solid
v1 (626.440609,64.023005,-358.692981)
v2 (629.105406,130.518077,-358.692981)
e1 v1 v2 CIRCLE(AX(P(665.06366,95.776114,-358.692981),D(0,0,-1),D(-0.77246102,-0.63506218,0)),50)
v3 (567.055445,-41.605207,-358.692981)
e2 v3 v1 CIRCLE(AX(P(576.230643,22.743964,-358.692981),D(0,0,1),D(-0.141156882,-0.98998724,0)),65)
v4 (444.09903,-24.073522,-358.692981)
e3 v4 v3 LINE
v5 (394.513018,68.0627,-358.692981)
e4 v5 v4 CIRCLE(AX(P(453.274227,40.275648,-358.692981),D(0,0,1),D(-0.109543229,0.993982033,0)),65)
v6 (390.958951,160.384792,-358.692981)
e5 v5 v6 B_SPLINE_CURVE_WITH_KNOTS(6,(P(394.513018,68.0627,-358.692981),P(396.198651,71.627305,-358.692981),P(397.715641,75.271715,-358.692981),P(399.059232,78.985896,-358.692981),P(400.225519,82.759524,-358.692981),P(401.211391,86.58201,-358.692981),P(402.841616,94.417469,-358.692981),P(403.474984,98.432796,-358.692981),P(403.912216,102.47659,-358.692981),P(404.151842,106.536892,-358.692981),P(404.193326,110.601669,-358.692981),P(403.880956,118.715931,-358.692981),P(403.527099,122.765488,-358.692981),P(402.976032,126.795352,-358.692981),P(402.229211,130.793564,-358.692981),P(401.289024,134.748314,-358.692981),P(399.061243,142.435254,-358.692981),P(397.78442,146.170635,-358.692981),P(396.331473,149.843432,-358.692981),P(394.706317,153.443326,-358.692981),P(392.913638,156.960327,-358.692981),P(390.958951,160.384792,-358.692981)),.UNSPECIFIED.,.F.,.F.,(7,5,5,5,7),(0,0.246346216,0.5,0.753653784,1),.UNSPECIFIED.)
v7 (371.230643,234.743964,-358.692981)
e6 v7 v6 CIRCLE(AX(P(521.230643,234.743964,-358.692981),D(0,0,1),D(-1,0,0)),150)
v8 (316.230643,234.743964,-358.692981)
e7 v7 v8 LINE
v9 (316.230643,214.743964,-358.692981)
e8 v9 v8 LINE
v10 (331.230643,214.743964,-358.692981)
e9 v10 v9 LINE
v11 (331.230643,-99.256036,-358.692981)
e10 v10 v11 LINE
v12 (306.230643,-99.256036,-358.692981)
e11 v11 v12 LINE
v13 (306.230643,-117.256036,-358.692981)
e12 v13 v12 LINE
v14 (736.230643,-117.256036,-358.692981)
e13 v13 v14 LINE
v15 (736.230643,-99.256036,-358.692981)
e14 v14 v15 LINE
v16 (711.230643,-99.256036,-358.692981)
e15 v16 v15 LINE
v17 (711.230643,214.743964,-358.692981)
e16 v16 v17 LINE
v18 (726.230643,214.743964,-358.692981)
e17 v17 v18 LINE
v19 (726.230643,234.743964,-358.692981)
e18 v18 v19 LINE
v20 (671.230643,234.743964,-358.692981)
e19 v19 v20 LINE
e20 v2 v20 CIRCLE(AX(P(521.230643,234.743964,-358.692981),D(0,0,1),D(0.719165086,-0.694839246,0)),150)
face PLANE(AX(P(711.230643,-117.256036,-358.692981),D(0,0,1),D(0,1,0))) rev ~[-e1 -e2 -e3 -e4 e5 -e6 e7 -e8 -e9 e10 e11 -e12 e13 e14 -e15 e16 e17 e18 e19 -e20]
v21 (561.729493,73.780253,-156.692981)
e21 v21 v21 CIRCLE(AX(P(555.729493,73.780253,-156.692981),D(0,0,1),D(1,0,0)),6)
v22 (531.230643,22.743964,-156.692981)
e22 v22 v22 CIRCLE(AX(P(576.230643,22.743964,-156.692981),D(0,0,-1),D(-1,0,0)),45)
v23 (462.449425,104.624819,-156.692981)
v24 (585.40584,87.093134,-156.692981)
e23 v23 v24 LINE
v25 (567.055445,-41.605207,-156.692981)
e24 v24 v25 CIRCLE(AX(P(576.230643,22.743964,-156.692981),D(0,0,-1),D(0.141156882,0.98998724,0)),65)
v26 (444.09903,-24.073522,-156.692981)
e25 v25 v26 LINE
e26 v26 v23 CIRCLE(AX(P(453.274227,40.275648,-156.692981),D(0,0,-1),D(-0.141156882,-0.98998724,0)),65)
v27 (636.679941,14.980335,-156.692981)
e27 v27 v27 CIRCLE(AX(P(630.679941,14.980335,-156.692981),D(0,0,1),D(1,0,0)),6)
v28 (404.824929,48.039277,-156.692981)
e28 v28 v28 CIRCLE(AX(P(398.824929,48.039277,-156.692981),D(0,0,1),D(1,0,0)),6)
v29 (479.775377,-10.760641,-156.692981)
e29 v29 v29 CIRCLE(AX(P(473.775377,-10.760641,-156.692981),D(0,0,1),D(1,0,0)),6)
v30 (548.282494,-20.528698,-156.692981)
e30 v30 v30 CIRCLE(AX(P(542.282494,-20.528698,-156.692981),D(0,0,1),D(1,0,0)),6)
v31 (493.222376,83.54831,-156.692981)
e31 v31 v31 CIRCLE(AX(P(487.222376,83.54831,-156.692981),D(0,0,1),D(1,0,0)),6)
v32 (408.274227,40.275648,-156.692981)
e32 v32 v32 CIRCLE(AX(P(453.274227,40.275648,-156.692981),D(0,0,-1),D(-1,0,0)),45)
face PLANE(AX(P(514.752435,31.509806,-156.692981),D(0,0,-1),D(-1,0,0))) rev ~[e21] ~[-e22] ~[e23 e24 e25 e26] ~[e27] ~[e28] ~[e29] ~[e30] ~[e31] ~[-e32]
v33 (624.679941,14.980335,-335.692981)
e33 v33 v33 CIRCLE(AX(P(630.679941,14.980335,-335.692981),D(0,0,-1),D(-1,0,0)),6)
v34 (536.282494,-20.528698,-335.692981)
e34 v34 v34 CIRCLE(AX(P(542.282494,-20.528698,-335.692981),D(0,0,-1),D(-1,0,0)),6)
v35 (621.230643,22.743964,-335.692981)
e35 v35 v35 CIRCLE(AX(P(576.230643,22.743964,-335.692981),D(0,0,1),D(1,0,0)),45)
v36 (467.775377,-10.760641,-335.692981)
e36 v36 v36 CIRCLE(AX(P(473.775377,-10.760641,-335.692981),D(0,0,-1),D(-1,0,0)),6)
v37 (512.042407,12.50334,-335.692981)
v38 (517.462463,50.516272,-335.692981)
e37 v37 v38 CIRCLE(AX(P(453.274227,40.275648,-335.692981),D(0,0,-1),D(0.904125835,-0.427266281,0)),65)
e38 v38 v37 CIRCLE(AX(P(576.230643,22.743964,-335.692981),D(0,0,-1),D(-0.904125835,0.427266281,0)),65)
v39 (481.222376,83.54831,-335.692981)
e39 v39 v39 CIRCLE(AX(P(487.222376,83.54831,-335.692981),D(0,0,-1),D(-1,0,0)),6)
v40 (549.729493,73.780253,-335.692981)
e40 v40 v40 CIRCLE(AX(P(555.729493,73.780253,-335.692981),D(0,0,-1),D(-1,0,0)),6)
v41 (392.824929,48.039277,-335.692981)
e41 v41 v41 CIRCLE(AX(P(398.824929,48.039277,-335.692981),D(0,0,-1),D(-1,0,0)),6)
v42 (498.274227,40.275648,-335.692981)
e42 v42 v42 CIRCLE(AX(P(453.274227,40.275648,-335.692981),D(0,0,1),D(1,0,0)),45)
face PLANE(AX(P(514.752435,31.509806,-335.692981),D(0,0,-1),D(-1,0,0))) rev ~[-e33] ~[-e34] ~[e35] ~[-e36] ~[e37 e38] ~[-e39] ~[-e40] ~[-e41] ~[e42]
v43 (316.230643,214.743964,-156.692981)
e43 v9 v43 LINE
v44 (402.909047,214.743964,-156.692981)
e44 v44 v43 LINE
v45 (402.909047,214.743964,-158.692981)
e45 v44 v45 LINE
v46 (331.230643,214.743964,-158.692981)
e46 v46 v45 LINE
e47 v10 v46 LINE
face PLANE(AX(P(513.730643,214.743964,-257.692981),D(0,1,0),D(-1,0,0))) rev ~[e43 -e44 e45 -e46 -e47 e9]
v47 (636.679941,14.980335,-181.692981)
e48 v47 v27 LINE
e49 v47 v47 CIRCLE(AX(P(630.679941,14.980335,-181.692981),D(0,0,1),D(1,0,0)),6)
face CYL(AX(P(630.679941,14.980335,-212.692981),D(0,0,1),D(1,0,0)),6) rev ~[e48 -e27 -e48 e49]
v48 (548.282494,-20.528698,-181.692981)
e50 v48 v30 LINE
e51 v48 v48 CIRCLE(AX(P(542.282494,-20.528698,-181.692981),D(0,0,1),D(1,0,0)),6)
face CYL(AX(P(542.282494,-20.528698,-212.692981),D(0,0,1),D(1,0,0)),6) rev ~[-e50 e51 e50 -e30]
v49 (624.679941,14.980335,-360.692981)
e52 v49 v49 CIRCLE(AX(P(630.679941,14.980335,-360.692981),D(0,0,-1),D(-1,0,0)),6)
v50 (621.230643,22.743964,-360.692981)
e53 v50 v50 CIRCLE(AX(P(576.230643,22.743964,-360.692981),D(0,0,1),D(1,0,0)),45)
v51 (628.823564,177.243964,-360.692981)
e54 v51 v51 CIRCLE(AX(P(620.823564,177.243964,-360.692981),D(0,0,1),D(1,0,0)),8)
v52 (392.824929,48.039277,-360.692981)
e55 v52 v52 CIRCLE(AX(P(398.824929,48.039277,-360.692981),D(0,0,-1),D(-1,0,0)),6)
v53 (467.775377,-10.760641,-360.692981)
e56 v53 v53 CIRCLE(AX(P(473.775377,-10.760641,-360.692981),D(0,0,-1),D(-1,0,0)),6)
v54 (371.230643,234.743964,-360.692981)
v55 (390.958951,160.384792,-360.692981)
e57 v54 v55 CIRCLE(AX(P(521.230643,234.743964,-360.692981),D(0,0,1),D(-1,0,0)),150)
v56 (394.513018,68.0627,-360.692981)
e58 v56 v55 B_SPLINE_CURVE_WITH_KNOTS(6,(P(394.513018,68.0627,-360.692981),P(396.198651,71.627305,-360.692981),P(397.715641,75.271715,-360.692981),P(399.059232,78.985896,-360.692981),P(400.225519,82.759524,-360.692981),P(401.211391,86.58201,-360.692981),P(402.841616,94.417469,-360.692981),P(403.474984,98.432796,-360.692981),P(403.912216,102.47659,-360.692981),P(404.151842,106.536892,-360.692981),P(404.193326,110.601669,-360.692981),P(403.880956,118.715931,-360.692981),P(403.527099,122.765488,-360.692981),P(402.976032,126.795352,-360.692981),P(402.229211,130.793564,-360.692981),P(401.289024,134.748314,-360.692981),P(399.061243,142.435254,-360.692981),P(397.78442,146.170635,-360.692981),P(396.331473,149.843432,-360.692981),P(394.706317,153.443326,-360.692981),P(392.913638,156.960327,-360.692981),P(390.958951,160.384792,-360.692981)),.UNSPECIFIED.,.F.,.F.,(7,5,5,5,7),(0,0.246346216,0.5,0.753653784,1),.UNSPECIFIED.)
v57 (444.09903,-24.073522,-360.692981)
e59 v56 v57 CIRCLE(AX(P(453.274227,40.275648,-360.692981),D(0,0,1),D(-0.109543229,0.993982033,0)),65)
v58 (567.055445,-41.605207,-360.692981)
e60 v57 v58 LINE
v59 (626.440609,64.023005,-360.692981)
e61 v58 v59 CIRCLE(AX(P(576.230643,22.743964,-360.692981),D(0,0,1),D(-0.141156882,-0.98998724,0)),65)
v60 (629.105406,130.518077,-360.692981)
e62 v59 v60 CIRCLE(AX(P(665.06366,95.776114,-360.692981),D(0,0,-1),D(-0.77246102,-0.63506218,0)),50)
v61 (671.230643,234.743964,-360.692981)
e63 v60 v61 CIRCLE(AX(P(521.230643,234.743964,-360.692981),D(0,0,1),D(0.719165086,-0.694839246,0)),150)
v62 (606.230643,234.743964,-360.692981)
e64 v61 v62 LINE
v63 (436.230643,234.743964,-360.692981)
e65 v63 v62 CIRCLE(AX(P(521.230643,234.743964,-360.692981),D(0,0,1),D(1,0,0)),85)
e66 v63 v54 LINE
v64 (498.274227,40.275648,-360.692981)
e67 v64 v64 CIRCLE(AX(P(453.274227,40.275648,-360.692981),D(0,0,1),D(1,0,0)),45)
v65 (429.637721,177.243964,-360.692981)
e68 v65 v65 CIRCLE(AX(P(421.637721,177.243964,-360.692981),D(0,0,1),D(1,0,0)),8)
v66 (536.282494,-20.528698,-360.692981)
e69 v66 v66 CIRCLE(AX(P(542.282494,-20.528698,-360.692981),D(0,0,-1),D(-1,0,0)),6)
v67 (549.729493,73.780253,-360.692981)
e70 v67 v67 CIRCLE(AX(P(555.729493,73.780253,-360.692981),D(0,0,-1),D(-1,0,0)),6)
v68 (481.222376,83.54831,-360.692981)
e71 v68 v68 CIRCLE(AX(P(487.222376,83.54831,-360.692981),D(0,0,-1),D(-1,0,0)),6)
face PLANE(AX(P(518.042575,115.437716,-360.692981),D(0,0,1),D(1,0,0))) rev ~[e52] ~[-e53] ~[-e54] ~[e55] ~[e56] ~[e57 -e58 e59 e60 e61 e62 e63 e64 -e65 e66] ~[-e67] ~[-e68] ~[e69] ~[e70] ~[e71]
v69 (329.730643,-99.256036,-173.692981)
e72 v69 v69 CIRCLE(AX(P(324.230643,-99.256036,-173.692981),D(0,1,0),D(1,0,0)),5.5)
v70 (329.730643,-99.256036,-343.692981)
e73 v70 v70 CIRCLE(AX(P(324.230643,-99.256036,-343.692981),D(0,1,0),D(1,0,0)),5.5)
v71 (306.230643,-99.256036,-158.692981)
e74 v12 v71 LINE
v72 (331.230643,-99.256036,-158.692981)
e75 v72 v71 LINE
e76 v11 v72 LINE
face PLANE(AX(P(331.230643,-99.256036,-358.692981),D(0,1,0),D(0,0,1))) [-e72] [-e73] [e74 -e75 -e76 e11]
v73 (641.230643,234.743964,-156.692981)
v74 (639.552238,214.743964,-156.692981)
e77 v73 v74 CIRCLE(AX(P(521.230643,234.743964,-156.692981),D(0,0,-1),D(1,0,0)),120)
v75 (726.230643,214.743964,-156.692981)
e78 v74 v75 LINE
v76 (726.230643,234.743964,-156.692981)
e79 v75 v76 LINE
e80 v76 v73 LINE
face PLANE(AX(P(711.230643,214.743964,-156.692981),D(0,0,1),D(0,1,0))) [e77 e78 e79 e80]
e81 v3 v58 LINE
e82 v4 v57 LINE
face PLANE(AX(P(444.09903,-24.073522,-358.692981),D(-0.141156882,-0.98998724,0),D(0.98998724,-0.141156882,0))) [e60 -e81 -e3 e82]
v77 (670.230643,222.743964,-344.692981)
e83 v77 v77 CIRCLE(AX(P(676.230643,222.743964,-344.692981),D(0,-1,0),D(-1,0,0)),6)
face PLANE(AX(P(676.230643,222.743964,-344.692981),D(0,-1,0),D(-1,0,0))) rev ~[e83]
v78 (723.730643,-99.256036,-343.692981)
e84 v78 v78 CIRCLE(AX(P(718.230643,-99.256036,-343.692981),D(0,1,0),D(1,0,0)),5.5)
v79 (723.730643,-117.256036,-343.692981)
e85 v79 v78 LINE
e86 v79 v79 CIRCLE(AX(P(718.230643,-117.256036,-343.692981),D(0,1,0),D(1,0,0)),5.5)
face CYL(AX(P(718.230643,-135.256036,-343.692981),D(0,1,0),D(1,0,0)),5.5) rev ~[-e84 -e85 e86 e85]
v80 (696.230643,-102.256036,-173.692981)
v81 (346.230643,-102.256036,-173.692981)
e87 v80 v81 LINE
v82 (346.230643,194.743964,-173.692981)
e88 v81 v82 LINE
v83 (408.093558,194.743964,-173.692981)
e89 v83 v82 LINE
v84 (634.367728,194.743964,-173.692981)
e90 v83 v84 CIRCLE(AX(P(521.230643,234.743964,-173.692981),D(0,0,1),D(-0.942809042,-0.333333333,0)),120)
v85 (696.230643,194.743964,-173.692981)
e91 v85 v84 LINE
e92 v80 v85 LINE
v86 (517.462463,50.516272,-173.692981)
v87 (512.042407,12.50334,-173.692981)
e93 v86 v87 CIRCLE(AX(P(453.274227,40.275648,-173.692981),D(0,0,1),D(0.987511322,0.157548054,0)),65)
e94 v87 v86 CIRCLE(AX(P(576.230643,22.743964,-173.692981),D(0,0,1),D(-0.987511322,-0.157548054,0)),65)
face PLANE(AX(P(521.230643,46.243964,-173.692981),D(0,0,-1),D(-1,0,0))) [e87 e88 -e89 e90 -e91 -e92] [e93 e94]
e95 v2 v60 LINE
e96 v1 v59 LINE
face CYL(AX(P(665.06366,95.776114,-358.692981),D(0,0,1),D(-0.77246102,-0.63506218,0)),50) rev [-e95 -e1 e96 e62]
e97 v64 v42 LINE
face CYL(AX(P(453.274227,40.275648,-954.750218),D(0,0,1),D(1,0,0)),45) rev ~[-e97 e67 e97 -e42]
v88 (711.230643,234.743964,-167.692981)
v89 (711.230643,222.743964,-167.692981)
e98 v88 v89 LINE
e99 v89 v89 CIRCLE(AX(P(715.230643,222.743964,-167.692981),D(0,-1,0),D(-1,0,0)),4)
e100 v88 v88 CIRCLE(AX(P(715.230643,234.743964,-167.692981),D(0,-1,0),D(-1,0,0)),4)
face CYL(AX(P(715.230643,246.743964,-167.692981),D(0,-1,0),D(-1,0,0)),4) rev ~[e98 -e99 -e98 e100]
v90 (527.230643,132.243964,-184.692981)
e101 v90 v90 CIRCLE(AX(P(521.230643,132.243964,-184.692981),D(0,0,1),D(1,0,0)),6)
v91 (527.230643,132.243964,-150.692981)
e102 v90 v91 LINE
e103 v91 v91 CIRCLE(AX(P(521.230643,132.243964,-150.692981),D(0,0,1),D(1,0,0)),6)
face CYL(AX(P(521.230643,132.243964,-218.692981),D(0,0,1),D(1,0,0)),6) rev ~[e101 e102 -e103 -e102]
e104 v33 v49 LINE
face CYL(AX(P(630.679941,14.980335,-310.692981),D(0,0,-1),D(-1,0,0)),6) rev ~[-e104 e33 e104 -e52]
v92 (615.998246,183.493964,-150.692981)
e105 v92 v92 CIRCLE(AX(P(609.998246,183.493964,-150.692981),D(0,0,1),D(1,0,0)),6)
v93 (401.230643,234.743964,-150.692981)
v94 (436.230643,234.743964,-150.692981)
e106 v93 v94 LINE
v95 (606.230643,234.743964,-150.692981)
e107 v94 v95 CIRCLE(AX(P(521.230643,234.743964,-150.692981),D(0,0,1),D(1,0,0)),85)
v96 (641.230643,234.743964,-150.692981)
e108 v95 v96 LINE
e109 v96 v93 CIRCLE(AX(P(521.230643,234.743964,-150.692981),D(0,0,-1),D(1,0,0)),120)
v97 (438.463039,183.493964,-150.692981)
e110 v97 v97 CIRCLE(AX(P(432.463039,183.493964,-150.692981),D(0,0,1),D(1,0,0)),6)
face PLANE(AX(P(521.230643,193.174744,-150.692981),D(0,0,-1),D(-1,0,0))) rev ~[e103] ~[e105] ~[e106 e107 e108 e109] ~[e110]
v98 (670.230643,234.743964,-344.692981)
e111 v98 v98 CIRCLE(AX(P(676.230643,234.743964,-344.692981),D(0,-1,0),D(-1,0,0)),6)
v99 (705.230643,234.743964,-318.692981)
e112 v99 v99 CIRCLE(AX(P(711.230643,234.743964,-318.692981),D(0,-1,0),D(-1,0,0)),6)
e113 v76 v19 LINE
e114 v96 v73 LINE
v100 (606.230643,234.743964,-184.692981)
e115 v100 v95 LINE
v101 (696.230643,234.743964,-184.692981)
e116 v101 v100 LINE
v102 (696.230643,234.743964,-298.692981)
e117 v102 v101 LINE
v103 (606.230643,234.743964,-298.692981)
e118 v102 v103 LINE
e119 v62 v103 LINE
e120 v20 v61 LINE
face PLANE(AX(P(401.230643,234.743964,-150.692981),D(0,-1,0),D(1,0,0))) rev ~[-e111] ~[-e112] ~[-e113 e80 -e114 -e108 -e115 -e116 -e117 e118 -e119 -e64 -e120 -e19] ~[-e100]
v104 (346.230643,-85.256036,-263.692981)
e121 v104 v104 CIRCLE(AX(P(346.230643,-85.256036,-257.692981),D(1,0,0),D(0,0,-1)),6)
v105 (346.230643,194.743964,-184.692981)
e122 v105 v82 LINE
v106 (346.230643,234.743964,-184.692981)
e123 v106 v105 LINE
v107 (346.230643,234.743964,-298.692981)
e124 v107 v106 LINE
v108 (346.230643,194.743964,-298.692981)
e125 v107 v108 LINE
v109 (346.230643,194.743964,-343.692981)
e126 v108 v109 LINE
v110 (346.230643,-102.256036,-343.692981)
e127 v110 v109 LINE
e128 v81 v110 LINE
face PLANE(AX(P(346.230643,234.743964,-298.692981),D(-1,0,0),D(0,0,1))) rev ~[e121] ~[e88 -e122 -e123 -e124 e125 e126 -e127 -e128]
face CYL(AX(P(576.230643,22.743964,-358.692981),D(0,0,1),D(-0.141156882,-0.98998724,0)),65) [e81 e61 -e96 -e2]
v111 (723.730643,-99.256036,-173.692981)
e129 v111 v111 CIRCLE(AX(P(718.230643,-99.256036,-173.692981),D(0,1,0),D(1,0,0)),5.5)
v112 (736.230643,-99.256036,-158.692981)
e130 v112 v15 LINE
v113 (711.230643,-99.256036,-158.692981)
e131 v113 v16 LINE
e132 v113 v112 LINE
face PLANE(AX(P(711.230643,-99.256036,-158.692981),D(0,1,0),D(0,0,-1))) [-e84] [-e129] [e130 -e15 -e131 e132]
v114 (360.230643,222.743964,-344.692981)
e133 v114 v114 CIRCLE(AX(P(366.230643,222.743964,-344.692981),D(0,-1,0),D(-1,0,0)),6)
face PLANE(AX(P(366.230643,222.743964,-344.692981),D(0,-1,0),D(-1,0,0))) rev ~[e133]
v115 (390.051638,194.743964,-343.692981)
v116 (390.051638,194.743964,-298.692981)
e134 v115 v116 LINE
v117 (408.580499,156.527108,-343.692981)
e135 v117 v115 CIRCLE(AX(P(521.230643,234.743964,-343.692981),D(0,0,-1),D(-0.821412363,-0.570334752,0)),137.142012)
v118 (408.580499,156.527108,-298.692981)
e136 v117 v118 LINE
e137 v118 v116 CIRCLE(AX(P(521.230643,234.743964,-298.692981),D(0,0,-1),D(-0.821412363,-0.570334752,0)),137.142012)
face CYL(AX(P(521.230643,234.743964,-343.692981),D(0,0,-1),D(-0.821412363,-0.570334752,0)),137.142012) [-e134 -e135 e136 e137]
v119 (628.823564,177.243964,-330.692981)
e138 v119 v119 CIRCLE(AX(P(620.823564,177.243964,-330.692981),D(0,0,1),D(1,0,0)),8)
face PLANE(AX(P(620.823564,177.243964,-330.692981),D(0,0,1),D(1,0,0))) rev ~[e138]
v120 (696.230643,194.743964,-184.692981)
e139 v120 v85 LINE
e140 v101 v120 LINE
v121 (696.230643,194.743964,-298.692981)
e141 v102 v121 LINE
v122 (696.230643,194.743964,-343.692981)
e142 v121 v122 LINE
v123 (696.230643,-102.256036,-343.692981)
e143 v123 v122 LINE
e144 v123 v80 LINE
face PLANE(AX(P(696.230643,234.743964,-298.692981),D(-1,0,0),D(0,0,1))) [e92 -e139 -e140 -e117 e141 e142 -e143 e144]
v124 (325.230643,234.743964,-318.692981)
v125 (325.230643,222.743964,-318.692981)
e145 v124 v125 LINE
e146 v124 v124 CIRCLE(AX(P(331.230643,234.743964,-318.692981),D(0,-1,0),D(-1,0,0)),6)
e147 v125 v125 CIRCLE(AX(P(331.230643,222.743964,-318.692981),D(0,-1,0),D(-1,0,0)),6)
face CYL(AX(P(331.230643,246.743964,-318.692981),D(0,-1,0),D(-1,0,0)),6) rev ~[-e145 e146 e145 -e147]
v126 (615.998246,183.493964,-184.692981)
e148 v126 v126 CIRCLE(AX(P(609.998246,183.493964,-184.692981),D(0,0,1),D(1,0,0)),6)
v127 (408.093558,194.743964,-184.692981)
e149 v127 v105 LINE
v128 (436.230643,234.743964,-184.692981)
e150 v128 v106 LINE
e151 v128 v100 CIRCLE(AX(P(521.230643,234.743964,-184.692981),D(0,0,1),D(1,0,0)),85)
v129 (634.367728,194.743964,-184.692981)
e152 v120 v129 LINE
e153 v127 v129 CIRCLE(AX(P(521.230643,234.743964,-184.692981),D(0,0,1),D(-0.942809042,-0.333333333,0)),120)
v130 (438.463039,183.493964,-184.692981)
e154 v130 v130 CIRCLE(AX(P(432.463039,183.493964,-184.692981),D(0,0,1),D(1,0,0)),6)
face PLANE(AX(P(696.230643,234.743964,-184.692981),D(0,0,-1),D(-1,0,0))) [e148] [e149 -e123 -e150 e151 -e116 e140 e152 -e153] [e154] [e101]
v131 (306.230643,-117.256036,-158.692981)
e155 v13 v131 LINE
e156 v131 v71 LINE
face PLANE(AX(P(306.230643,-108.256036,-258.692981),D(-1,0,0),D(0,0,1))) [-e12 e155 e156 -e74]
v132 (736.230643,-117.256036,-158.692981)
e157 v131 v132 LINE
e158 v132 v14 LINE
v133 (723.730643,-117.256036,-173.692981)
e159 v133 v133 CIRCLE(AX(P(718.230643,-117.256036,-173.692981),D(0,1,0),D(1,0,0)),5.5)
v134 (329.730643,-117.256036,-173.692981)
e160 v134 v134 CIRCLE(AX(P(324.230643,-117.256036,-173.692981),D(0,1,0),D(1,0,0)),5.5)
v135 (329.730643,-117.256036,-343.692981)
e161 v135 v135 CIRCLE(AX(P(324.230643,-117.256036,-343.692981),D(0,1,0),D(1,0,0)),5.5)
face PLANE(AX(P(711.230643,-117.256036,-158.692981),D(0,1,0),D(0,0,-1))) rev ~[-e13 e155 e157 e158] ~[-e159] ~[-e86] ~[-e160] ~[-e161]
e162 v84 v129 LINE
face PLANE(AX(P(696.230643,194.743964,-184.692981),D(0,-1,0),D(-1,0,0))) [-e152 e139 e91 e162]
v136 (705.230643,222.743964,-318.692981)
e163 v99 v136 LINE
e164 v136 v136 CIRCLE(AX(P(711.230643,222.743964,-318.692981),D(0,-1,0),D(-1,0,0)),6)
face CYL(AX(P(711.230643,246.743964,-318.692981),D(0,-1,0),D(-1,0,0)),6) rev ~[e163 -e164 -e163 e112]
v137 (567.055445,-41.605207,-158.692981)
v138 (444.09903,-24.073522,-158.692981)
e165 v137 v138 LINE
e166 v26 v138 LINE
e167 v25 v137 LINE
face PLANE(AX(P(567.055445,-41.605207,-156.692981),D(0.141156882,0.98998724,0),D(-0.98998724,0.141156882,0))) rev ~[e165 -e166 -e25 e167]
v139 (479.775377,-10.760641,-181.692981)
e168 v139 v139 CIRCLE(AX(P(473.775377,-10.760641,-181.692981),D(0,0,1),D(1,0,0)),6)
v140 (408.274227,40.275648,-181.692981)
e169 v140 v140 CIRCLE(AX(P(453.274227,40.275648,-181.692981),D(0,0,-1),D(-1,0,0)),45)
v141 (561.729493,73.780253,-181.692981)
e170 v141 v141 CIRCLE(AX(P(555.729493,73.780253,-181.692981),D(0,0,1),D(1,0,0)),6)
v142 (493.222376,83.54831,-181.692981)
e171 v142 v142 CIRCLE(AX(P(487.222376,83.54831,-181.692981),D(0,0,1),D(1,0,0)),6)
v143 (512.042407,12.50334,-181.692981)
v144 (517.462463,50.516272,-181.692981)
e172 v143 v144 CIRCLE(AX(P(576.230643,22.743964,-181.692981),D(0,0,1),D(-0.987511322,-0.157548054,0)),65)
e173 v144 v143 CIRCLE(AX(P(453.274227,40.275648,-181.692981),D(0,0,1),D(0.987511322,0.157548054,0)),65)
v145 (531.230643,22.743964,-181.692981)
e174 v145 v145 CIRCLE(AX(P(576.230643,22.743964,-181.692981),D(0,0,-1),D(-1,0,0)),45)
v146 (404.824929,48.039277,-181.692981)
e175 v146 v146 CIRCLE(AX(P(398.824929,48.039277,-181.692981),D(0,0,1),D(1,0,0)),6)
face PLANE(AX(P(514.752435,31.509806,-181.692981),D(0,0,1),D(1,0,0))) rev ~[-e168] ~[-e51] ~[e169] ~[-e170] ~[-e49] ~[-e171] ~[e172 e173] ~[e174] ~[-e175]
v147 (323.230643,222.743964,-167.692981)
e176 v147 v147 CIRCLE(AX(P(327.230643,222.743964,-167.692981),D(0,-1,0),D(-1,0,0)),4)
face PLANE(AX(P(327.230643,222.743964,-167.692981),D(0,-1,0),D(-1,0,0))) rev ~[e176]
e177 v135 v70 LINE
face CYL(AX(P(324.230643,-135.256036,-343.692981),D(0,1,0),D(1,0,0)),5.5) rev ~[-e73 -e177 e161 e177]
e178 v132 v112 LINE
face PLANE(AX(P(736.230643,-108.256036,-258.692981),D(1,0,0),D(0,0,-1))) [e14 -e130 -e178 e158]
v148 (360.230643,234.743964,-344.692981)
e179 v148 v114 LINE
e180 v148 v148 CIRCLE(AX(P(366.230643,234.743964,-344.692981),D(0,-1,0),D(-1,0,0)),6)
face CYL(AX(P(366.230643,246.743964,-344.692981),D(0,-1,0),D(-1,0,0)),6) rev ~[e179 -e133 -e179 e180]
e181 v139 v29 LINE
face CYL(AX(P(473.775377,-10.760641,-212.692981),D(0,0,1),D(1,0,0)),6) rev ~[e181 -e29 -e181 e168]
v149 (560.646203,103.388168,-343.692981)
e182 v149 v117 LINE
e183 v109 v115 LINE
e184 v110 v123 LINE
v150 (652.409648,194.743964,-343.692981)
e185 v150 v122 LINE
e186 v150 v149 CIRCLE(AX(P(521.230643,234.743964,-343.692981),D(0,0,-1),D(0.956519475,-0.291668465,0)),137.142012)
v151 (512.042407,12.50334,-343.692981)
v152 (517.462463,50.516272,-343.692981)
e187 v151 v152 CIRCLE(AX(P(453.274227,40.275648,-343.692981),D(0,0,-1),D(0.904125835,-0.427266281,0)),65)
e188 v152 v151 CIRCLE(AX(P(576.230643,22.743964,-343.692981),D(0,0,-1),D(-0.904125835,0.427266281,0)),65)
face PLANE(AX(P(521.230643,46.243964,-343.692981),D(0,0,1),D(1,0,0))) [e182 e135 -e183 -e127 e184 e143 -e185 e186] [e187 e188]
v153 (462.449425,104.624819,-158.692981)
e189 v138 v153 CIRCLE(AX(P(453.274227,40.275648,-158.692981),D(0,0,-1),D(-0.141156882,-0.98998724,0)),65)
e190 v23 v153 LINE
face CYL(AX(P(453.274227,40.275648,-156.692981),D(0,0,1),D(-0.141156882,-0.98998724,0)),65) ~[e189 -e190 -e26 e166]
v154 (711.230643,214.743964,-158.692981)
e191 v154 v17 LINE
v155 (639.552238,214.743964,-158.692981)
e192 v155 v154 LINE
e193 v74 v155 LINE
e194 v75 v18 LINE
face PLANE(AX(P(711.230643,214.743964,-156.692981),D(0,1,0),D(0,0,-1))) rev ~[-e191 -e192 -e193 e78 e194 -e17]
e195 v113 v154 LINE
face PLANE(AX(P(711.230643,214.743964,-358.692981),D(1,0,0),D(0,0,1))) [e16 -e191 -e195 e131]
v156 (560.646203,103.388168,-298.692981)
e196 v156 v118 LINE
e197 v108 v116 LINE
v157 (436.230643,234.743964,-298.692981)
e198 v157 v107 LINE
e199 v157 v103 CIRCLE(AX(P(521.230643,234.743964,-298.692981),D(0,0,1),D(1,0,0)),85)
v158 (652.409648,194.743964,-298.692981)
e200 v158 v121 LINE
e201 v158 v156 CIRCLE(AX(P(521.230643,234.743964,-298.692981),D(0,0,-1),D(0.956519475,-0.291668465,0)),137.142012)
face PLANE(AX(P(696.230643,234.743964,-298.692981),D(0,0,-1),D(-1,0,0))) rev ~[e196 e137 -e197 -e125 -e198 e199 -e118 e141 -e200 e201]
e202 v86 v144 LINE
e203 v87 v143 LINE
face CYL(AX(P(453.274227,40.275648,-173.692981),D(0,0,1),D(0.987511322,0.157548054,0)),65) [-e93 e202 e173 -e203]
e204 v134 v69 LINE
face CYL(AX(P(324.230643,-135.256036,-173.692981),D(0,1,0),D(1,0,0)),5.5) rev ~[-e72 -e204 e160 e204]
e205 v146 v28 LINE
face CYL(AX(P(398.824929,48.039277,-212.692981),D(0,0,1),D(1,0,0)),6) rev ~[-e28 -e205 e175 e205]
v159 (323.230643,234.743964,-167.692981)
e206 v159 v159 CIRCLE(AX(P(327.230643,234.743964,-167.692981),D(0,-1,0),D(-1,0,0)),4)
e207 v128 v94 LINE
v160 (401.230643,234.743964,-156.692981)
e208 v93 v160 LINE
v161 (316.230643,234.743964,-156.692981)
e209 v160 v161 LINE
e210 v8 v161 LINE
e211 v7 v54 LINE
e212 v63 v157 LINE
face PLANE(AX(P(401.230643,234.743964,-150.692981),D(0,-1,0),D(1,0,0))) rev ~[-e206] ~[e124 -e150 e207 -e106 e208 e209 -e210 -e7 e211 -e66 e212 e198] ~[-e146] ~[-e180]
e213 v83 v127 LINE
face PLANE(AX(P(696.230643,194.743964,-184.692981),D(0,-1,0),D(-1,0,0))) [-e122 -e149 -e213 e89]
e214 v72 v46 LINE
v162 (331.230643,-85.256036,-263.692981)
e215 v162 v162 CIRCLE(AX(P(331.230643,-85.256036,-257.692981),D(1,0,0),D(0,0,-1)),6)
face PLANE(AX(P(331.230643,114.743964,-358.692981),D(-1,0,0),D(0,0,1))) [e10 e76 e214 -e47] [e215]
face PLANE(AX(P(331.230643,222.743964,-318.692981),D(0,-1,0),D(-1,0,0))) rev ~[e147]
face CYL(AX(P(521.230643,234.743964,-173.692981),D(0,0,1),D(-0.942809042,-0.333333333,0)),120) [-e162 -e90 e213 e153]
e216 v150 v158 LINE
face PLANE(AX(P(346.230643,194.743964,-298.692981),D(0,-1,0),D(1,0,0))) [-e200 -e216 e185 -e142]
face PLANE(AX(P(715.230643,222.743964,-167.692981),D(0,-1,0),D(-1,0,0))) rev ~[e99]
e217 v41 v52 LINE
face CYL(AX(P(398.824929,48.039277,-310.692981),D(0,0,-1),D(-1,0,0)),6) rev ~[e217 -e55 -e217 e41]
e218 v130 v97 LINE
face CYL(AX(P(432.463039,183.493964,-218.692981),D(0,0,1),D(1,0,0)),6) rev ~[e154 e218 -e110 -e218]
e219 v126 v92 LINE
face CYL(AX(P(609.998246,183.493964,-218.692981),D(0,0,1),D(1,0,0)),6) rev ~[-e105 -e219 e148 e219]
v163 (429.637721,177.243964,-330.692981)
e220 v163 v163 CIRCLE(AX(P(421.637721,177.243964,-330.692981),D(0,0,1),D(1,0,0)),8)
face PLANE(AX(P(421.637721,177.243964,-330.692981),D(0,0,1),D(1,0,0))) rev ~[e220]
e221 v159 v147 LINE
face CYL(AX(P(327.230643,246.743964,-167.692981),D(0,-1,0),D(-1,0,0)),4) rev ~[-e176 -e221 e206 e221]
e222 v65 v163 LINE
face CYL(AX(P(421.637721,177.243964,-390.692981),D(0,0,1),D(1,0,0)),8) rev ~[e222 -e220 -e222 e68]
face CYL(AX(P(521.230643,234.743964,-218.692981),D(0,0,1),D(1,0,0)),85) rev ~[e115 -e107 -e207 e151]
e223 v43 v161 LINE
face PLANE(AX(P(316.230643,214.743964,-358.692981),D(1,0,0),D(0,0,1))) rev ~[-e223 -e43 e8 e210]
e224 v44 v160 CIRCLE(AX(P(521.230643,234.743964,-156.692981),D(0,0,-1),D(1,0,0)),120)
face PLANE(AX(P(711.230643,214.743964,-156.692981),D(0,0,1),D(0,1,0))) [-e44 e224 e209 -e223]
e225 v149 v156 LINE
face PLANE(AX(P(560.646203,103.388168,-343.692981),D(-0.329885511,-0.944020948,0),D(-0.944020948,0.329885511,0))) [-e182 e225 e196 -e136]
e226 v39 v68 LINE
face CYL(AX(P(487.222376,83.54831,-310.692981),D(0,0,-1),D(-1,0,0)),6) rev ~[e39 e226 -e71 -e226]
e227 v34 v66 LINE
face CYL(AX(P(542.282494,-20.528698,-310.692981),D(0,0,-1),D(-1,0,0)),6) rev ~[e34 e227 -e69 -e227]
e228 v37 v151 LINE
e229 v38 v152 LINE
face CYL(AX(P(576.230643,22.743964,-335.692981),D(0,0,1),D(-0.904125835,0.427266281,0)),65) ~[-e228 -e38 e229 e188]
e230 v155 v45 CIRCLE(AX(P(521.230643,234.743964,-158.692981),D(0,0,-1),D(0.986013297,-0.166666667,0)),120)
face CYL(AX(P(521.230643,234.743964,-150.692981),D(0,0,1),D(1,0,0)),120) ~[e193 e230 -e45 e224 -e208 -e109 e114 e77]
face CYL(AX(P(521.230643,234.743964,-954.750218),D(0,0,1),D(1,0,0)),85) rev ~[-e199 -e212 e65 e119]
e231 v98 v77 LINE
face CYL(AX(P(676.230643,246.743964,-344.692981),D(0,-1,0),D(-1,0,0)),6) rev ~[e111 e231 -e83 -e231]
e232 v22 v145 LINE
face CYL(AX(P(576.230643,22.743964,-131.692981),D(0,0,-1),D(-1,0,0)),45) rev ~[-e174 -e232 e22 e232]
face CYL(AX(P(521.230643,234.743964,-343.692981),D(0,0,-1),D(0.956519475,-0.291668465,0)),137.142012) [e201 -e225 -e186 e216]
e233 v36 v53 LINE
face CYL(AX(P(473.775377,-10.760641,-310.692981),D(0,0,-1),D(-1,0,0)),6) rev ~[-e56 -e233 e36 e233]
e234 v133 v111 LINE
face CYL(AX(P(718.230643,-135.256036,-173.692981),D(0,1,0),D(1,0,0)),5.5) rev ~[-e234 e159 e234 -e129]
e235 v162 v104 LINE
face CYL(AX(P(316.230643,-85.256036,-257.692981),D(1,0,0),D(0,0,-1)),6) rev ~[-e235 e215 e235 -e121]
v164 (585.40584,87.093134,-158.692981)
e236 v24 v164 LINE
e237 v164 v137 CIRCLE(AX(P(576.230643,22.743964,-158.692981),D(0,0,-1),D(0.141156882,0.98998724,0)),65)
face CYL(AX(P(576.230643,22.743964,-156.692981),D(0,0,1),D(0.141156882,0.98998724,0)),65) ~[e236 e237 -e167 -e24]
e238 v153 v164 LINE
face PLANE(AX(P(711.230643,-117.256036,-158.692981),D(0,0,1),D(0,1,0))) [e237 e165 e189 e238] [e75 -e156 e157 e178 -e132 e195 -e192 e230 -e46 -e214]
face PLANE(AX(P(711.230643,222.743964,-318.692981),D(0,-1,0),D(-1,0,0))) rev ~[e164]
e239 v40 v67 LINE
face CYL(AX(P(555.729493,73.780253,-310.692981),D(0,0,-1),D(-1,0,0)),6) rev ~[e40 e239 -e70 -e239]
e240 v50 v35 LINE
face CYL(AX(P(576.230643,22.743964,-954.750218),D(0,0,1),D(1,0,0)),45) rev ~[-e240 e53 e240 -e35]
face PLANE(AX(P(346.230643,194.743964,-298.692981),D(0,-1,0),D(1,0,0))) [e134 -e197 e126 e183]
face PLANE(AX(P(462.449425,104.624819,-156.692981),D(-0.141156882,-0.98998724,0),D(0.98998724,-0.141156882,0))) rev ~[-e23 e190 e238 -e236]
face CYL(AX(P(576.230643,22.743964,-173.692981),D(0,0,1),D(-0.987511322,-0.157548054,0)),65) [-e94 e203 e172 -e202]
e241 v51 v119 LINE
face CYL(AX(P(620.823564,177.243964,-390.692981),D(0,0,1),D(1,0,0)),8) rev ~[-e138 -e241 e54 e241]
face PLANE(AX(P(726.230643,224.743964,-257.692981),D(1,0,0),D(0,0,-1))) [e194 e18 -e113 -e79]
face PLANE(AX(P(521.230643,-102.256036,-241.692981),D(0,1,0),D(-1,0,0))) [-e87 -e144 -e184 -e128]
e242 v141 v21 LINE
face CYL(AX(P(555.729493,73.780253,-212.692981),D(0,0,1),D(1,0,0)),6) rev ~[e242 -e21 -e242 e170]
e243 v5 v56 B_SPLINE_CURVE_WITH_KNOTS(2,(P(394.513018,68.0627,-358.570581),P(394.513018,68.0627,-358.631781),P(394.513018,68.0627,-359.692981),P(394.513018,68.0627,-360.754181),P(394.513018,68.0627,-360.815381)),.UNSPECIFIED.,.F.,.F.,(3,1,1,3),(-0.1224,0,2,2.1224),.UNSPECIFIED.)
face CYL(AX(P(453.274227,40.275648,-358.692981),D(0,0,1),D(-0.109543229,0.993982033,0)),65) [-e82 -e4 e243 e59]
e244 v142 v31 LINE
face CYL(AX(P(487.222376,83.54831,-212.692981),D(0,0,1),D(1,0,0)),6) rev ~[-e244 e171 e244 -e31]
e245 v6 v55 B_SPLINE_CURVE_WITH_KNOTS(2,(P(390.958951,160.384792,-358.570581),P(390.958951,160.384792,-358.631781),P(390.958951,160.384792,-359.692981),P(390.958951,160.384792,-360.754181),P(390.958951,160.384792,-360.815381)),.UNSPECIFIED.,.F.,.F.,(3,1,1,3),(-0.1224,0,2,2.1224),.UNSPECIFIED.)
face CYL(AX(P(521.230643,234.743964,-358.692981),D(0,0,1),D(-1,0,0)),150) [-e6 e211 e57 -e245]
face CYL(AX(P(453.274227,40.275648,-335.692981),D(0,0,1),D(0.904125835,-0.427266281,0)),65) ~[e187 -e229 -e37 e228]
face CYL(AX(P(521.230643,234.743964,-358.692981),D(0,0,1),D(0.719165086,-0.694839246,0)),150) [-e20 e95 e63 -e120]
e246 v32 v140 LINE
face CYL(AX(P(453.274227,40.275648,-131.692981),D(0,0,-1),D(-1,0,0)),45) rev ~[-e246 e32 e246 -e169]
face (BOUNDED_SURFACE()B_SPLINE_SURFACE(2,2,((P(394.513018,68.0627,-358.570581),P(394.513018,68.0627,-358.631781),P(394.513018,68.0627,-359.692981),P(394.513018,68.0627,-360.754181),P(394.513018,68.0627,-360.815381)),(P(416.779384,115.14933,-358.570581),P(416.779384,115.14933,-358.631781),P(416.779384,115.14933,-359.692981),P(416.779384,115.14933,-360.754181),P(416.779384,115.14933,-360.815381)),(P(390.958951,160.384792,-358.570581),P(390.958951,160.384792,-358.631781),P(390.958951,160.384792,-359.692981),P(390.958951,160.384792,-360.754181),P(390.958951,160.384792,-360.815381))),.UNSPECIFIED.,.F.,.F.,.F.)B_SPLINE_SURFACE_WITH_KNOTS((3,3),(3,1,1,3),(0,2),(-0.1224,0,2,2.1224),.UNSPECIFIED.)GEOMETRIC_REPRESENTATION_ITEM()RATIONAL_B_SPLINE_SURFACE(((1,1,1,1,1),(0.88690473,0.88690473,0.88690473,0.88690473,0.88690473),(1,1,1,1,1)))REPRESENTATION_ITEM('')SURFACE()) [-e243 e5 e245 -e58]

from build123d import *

# Parameters (mm, degrees)
BOSS_EXTRUDE1_DEPTH            = 2
BOSS_EXTRUDE2_DEPTH            = 100
SKETCH3_W                      = 380
SKETCH3_H                      = 200
BOSS_EXTRUDE3_DEPTH            = 232
SKETCH4_W                      = 395
SKETCH4_H                      = 202
BOSS_EXTRUDE4_DEPTH            = 20
SKETCH5_W                      = 202
SKETCH5_H                      = 20
BOSS_EXTRUDE5_DEPTH            = 15
BOSS_EXTRUDE6_START            = 6
BOSS_EXTRUDE6_DEPTH            = 6
SKETCH7_W                      = 200
SKETCH7_H                      = 18
BOSS_EXTRUDE7_DEPTH            = 25
SKETCH8_W                      = 200
SKETCH8_H                      = 18
BOSS_EXTRUDE8_DEPTH            = 25
SKETCH9_W                      = 350
SKETCH9_H                      = 114
CUT_EXTRUDE1_DEPTH             = 337
SKETCH10_W                     = 350
SKETCH10_H                     = 297
CUT_EXTRUDE2_DEPTH             = 45
SKETCH11_W                     = 350
SKETCH11_H                     = 297
CUT_EXTRUDE3_DEPTH             = 11
BOSS_EXTRUDE9_DEPTH            = 2
BOSS_EXTRUDE10_DEPTH           = 45
BOSS_EXTRUDE11_DEPTH           = 11
BOSS_EXTRUDE12_START           = 2
BOSS_EXTRUDE12_DEPTH           = 2
BOSS_EXTRUDE13_START           = 8
BOSS_EXTRUDE13_DEPTH           = 8
BOSS_EXTRUDE14_DEPTH           = 8
F_16_0_16_DIAMETER_HOLE1_D     = 16
F_16_0_16_DIAMETER_HOLE1_DEPTH = 30
F_12_0_12_DIAMETER_HOLE1_D     = 12
F_12_0_12_DIAMETER_HOLE1_DEPTH = 34
HOLE1_D                        = 170
HOLE1_DEPTH                    = 34
HOLE2_D                        = 170
F_11_0_11_DIAMETER_HOLE1_D     = 11
F_11_0_11_DIAMETER_HOLE1_DEPTH = 18
F_12_0_12_DIAMETER_HOLE2_D     = 12
F_12_0_12_DIAMETER_HOLE2_DEPTH = 12
F_8_0_8_DIAMETER_HOLE1_D       = 8
F_8_0_8_DIAMETER_HOLE1_DEPTH   = 12
F_12_0_12_DIAMETER_HOLE3_D     = 12
F_12_0_12_DIAMETER_HOLE3_DEPTH = 15
F_12_0_12_DIAMETER_HOLE4_D     = 12
F_12_0_12_DIAMETER_HOLE4_DEPTH = 25
F_12_0_12_DIAMETER_HOLE5_D     = 12
F_12_0_12_DIAMETER_HOLE5_DEPTH = 31
M80_CLEARANCE_HOLE1_D          = 90
M80_CLEARANCE_HOLE1_DEPTH      = 25
M80_CLEARANCE_HOLE2_D          = 90
FILLET1_R                      = 100


with BuildPart() as part:
    # Sketch1 → Boss-Extrude1 (new body)
    with BuildSketch(Plane.XY.offset(-156.692981355)):
        with BuildLine():
            Line((639.552238246, 214.743963655), (402.909046922, 214.743963655))
            ThreePointArc((402.909046922, 214.743963655), (521.230642584, 114.743963655), (639.552238246, 214.743963655))
        make_face()
    extrude(amount=-BOSS_EXTRUDE1_DEPTH)

    # Sketch2 → Boss-Extrude2 (add)
    with BuildSketch(Plane(origin=(0, 214.743963655, 0), x_dir=(1, 0, 0), z_dir=(0, 1, 0))):
        Polygon((331.230642584, 158.692981355), (521.230642584, 158.692981355), (711.230642584, 158.692981355), (711.230642584, 358.692981355), (331.230642584, 358.692981355), align=None)
    extrude(amount=-BOSS_EXTRUDE2_DEPTH)

    # Sketch3 → Boss-Extrude3 (add)
    with BuildSketch(Plane.XZ.offset(-114.743963655)):
        with Locations((521.230642584, -258.692981355)):
            Rectangle(SKETCH3_W, SKETCH3_H)
    extrude(amount=BOSS_EXTRUDE3_DEPTH)

    # Sketch4 → Boss-Extrude4 (add)
    with BuildSketch(Plane(origin=(0, 214.743963655, 0), x_dir=(-1, 0, 0), z_dir=(0, 1, 0))):
        with Locations((-513.730642584, -257.692981355)):
            Rectangle(SKETCH4_W, SKETCH4_H)
    extrude(amount=BOSS_EXTRUDE4_DEPTH)

    # Sketch5 → Boss-Extrude5 (add)
    with BuildSketch(Plane(origin=(711.230642584, 0, 0), x_dir=(0, 0, -1), z_dir=(1, 0, 0))):
        with Locations((257.692981355, 224.743963655)):
            Rectangle(SKETCH5_W, SKETCH5_H)
    extrude(amount=BOSS_EXTRUDE5_DEPTH)

    # Sketch6 → Boss-Extrude6 (add)
    with BuildSketch(Plane.XY.offset(-156.692981355).offset(BOSS_EXTRUDE6_START)):
        with BuildLine():
            Line((401.230642584, 234.743963655), (641.230642584, 234.743963655))
            ThreePointArc((641.230642584, 234.743963655), (521.230642584, 114.743963655), (401.230642584, 234.743963655))
        make_face()
    extrude(amount=-BOSS_EXTRUDE6_DEPTH)

    # Sketch7 → Boss-Extrude7 (add)
    with BuildSketch(Plane.ZY.offset(-331.230642584)):
        with Locations((-258.692981355, -108.256036345)):
            Rectangle(SKETCH7_W, SKETCH7_H)
    extrude(amount=BOSS_EXTRUDE7_DEPTH)

    # Sketch8 → Boss-Extrude8 (add)
    with BuildSketch(Plane(origin=(711.230642584, 0, 0), x_dir=(0, 0, -1), z_dir=(1, 0, 0))):
        with Locations((258.692981355, -108.256036345)):
            Rectangle(SKETCH8_W, SKETCH8_H)
    extrude(amount=BOSS_EXTRUDE8_DEPTH)

    # Sketch9 → Cut-Extrude1 (cut)
    with BuildSketch(Plane(origin=(0, 234.743963655, 0), x_dir=(-1, 0, 0), z_dir=(0, 1, 0))):
        with Locations((-521.230642584, -241.692981355)):
            Rectangle(SKETCH9_W, SKETCH9_H)
    extrude(amount=-CUT_EXTRUDE1_DEPTH, mode=Mode.SUBTRACT)

    # Sketch10 → Cut-Extrude2 (cut)
    with BuildSketch(Plane.XY.offset(-298.692981355)):
        with Locations((521.230642584, 46.243963655)):
            Rectangle(SKETCH10_W, SKETCH10_H)
    extrude(amount=-CUT_EXTRUDE2_DEPTH, mode=Mode.SUBTRACT)

    # Sketch11 → Cut-Extrude3 (cut)
    with BuildSketch(Plane(origin=(0, 0, -184.692981355), x_dir=(-1, 0, 0), z_dir=(0, 0, -1))):
        with Locations((-521.230642584, 46.243963655)):
            Rectangle(SKETCH11_W, SKETCH11_H)
    extrude(amount=-CUT_EXTRUDE3_DEPTH, mode=Mode.SUBTRACT)

    # Sketch12 → Boss-Extrude9 (add)
    with BuildSketch(Plane(origin=(0, 0, -358.692981355), x_dir=(-1, 0, 0), z_dir=(0, 0, -1))):
        with BuildLine():
            Line((-671.230642584, 234.743963655), (-371.230642584, 234.743963655))
            ThreePointArc((-371.230642584, 234.743963655), (-391.3046853, 159.782335979), (-446.153917567, 104.884480517))
            ThreePointArc((-446.153917567, 104.884480517), (-388.282477918, 41.311262548), (-444.09903009, -24.073522177))
            Line((-444.09903009, -24.073522177), (-567.055445254, -41.605206922))
            ThreePointArc((-567.055445254, -41.605206922), (-632.890089049, -9.110504263), (-626.440608883, 64.023005362))
            ThreePointArc((-626.440608883, 64.023005362), (-615.103761927, 97.778262306), (-629.105405557, 130.51807669))
            ThreePointArc((-629.105405557, 130.51807669), (-660.301154279, 178.53548763), (-671.230642584, 234.743963655))
        make_face()
    extrude(amount=BOSS_EXTRUDE9_DEPTH)

    # Sketch13 → Boss-Extrude10 (add)
    with BuildSketch(Plane.XY.offset(-343.692981355)):
        with BuildLine():
            Line((390.051637579, 194.743963655), (652.409647589, 194.743963655))
            ThreePointArc((652.409647589, 194.743963655), (617.988571356, 137.55428018), (560.64620314, 103.388168426))
            Line((560.64620314, 103.388168426), (408.580498696, 156.527108463))
            ThreePointArc((408.580498696, 156.527108463), (397.827662605, 174.913905269), (390.051637579, 194.743963655))
        make_face()
    extrude(amount=BOSS_EXTRUDE10_DEPTH)

    # Sketch14 → Boss-Extrude11 (add)
    with BuildSketch(Plane(origin=(0, 0, -173.692981355), x_dir=(-1, 0, 0), z_dir=(0, 0, -1))):
        with BuildLine():
            Line((-634.367727574, 194.743963655), (-408.093557595, 194.743963655))
            ThreePointArc((-408.093557595, 194.743963655), (-521.230642584, 114.743963655), (-634.367727574, 194.743963655))
        make_face()
    extrude(amount=BOSS_EXTRUDE11_DEPTH)

    # Sketch15 → Boss-Extrude12 (add)
    with BuildSketch(Plane.XY.offset(-158.692981355).offset(BOSS_EXTRUDE12_START)):
        with BuildLine():
            Line((462.449424751, 104.624818977), (585.405839915, 87.093134232))
            ThreePointArc((585.405839915, 87.093134232), (640.579813161, 13.568766324), (567.055445254, -41.605206922))
            Line((567.055445254, -41.605206922), (444.09903009, -24.073522177))
            ThreePointArc((444.09903009, -24.073522177), (388.925056843, 49.45084573), (462.449424751, 104.624818977))
        make_face()
    extrude(amount=-BOSS_EXTRUDE12_DEPTH)

    # Sketch16 → Boss-Extrude13 (add)
    with BuildSketch(Plane.XY.offset(-343.692981355).offset(BOSS_EXTRUDE13_START)):
        with BuildLine():
            ThreePointArc((517.462463333, 50.516271939), (640.579813161, 13.568766324), (512.042406672, 12.503340115))
            ThreePointArc((512.042406672, 12.503340115), (388.925056843, 49.45084573), (517.462463333, 50.516271939))
        make_face()
    extrude(amount=-BOSS_EXTRUDE13_DEPTH)

    # Sketch17 → Boss-Extrude14 (add)
    with BuildSketch(Plane(origin=(0, 0, -173.692981355), x_dir=(-1, 0, 0), z_dir=(0, 0, -1))):
        with BuildLine():
            ThreePointArc((-512.042406672, 12.503340115), (-640.579813161, 13.568766324), (-517.462463333, 50.516271939))
            ThreePointArc((-517.462463333, 50.516271939), (-388.925056843, 49.45084573), (-512.042406672, 12.503340115))
        make_face()
    extrude(amount=BOSS_EXTRUDE14_DEPTH)

    # Ø16.0 (16) diameter hole1
    with Locations(Plane(origin=(0, 0, -360.692981355), x_dir=(-1, 0, 0), z_dir=(0, 0, -1))):
        with Locations((-421.637721149, 177.243963655), (-620.82356402, 177.243963655)):
            Hole(F_16_0_16_DIAMETER_HOLE1_D / 2, depth=F_16_0_16_DIAMETER_HOLE1_DEPTH)

    # Ø12.0 (12) diameter hole1
    with Locations(Plane(origin=(0, 0, -184.692981355), x_dir=(-1, 0, 0), z_dir=(0, 0, -1))):
        with Locations((-521.230642584, 132.243963655), (-432.463038696, 183.493963655), (-609.998246472, 183.493963655)):
            Hole(F_12_0_12_DIAMETER_HOLE1_D / 2, depth=F_12_0_12_DIAMETER_HOLE1_DEPTH)

    # Hole1
    with Locations(Plane(origin=(0, 0, -184.692981355), x_dir=(-1, 0, 0), z_dir=(0, 0, -1))):
        with Locations((-521.230642584, 234.743963655)):
            Hole(HOLE1_D / 2, depth=HOLE1_DEPTH)

    # Hole2 (through all)
    with Locations(Plane(origin=(0, 0, -360.692981355), x_dir=(-1, 0, 0), z_dir=(0, 0, -1))):
        with Locations((-521.230642584, 234.743963655)):
            Hole(HOLE2_D / 2)

    # Ø11.0 (11) diameter hole1
    with Locations(Plane(origin=(0, -117.256036345, 0), x_dir=(-1, 0, 0), z_dir=(0, -1, 0))):
        with Locations((-718.230642584, 343.692981355), (-324.230642584, 343.692981355), (-324.230642584, 173.692981355), (-718.230642584, 173.692981355)):
            Hole(F_11_0_11_DIAMETER_HOLE1_D / 2, depth=F_11_0_11_DIAMETER_HOLE1_DEPTH)

    # Ø12.0 (12) diameter hole2
    with Locations(Plane(origin=(0, 234.743963655, 0), x_dir=(1, 0, 0), z_dir=(0, 1, 0))):
        with Locations((331.230642584, 318.692981355), (366.230642584, 344.692981355), (711.230642584, 318.692981355), (676.230642584, 344.692981355)):
            Hole(F_12_0_12_DIAMETER_HOLE2_D / 2, depth=F_12_0_12_DIAMETER_HOLE2_DEPTH)

    # Ø8.0 (8) diameter hole1
    with Locations(Plane(origin=(0, 234.743963655, 0), x_dir=(1, 0, 0), z_dir=(0, 1, 0))):
        with Locations((327.230642584, 167.692981355), (715.230642584, 167.692981355)):
            Hole(F_8_0_8_DIAMETER_HOLE1_D / 2, depth=F_8_0_8_DIAMETER_HOLE1_DEPTH)

    # Ø12.0 (12) diameter hole3
    with Locations(Plane.ZY.offset(-331.230642584)):
        with Locations((-257.692981355, -85.256036345)):
            Hole(F_12_0_12_DIAMETER_HOLE3_D / 2, depth=F_12_0_12_DIAMETER_HOLE3_DEPTH)

    # Ø12.0 (12) diameter hole4
    with Locations(Plane.XY.offset(-335.692981355)):
        with Locations((630.679940765, 14.980335144), (542.282493979, -20.528697533), (555.72949301, 73.780253352), (398.82492924, 48.03927691), (487.222376026, 83.548309587), (473.775376995, -10.760641298)):
            Hole(F_12_0_12_DIAMETER_HOLE4_D / 2, depth=F_12_0_12_DIAMETER_HOLE4_DEPTH)

    # Ø12.0 (12) diameter hole5
    with Locations(Plane(origin=(0, 0, -181.692981355), x_dir=(-1, 0, 0), z_dir=(0, 0, -1))):
        with Locations((-630.679940765, 14.980335144), (-555.72949301, 73.780253352), (-542.282493979, -20.528697533), (-398.82492924, 48.03927691), (-473.775376995, -10.760641298), (-487.222376026, 83.548309587)):
            Hole(F_12_0_12_DIAMETER_HOLE5_D / 2, depth=F_12_0_12_DIAMETER_HOLE5_DEPTH)

    # M80 clearance hole1
    with Locations(Plane.XY.offset(-156.692981355)):
        with Locations((453.27422742, 40.2756484), (576.230642584, 22.743963655)):
            Hole(M80_CLEARANCE_HOLE1_D / 2, depth=M80_CLEARANCE_HOLE1_DEPTH)

    # M80 clearance hole2 (through all)
    with Locations(Plane(origin=(0, 0, -360.692981355), x_dir=(-1, 0, 0), z_dir=(0, 0, -1))):
        with Locations((-453.27422742, 40.2756484), (-576.230642584, 22.743963655)):
            Hole(M80_CLEARANCE_HOLE2_D / 2)

    # Fillet1
    fillet1_edges = [part.edges().sort_by_distance(p)[0] for p in [
        (446.153917567, 104.884480517, -359.692981355),
    ]]
    fillet(fillet1_edges, radius=FILLET1_R)


solid = part.part
